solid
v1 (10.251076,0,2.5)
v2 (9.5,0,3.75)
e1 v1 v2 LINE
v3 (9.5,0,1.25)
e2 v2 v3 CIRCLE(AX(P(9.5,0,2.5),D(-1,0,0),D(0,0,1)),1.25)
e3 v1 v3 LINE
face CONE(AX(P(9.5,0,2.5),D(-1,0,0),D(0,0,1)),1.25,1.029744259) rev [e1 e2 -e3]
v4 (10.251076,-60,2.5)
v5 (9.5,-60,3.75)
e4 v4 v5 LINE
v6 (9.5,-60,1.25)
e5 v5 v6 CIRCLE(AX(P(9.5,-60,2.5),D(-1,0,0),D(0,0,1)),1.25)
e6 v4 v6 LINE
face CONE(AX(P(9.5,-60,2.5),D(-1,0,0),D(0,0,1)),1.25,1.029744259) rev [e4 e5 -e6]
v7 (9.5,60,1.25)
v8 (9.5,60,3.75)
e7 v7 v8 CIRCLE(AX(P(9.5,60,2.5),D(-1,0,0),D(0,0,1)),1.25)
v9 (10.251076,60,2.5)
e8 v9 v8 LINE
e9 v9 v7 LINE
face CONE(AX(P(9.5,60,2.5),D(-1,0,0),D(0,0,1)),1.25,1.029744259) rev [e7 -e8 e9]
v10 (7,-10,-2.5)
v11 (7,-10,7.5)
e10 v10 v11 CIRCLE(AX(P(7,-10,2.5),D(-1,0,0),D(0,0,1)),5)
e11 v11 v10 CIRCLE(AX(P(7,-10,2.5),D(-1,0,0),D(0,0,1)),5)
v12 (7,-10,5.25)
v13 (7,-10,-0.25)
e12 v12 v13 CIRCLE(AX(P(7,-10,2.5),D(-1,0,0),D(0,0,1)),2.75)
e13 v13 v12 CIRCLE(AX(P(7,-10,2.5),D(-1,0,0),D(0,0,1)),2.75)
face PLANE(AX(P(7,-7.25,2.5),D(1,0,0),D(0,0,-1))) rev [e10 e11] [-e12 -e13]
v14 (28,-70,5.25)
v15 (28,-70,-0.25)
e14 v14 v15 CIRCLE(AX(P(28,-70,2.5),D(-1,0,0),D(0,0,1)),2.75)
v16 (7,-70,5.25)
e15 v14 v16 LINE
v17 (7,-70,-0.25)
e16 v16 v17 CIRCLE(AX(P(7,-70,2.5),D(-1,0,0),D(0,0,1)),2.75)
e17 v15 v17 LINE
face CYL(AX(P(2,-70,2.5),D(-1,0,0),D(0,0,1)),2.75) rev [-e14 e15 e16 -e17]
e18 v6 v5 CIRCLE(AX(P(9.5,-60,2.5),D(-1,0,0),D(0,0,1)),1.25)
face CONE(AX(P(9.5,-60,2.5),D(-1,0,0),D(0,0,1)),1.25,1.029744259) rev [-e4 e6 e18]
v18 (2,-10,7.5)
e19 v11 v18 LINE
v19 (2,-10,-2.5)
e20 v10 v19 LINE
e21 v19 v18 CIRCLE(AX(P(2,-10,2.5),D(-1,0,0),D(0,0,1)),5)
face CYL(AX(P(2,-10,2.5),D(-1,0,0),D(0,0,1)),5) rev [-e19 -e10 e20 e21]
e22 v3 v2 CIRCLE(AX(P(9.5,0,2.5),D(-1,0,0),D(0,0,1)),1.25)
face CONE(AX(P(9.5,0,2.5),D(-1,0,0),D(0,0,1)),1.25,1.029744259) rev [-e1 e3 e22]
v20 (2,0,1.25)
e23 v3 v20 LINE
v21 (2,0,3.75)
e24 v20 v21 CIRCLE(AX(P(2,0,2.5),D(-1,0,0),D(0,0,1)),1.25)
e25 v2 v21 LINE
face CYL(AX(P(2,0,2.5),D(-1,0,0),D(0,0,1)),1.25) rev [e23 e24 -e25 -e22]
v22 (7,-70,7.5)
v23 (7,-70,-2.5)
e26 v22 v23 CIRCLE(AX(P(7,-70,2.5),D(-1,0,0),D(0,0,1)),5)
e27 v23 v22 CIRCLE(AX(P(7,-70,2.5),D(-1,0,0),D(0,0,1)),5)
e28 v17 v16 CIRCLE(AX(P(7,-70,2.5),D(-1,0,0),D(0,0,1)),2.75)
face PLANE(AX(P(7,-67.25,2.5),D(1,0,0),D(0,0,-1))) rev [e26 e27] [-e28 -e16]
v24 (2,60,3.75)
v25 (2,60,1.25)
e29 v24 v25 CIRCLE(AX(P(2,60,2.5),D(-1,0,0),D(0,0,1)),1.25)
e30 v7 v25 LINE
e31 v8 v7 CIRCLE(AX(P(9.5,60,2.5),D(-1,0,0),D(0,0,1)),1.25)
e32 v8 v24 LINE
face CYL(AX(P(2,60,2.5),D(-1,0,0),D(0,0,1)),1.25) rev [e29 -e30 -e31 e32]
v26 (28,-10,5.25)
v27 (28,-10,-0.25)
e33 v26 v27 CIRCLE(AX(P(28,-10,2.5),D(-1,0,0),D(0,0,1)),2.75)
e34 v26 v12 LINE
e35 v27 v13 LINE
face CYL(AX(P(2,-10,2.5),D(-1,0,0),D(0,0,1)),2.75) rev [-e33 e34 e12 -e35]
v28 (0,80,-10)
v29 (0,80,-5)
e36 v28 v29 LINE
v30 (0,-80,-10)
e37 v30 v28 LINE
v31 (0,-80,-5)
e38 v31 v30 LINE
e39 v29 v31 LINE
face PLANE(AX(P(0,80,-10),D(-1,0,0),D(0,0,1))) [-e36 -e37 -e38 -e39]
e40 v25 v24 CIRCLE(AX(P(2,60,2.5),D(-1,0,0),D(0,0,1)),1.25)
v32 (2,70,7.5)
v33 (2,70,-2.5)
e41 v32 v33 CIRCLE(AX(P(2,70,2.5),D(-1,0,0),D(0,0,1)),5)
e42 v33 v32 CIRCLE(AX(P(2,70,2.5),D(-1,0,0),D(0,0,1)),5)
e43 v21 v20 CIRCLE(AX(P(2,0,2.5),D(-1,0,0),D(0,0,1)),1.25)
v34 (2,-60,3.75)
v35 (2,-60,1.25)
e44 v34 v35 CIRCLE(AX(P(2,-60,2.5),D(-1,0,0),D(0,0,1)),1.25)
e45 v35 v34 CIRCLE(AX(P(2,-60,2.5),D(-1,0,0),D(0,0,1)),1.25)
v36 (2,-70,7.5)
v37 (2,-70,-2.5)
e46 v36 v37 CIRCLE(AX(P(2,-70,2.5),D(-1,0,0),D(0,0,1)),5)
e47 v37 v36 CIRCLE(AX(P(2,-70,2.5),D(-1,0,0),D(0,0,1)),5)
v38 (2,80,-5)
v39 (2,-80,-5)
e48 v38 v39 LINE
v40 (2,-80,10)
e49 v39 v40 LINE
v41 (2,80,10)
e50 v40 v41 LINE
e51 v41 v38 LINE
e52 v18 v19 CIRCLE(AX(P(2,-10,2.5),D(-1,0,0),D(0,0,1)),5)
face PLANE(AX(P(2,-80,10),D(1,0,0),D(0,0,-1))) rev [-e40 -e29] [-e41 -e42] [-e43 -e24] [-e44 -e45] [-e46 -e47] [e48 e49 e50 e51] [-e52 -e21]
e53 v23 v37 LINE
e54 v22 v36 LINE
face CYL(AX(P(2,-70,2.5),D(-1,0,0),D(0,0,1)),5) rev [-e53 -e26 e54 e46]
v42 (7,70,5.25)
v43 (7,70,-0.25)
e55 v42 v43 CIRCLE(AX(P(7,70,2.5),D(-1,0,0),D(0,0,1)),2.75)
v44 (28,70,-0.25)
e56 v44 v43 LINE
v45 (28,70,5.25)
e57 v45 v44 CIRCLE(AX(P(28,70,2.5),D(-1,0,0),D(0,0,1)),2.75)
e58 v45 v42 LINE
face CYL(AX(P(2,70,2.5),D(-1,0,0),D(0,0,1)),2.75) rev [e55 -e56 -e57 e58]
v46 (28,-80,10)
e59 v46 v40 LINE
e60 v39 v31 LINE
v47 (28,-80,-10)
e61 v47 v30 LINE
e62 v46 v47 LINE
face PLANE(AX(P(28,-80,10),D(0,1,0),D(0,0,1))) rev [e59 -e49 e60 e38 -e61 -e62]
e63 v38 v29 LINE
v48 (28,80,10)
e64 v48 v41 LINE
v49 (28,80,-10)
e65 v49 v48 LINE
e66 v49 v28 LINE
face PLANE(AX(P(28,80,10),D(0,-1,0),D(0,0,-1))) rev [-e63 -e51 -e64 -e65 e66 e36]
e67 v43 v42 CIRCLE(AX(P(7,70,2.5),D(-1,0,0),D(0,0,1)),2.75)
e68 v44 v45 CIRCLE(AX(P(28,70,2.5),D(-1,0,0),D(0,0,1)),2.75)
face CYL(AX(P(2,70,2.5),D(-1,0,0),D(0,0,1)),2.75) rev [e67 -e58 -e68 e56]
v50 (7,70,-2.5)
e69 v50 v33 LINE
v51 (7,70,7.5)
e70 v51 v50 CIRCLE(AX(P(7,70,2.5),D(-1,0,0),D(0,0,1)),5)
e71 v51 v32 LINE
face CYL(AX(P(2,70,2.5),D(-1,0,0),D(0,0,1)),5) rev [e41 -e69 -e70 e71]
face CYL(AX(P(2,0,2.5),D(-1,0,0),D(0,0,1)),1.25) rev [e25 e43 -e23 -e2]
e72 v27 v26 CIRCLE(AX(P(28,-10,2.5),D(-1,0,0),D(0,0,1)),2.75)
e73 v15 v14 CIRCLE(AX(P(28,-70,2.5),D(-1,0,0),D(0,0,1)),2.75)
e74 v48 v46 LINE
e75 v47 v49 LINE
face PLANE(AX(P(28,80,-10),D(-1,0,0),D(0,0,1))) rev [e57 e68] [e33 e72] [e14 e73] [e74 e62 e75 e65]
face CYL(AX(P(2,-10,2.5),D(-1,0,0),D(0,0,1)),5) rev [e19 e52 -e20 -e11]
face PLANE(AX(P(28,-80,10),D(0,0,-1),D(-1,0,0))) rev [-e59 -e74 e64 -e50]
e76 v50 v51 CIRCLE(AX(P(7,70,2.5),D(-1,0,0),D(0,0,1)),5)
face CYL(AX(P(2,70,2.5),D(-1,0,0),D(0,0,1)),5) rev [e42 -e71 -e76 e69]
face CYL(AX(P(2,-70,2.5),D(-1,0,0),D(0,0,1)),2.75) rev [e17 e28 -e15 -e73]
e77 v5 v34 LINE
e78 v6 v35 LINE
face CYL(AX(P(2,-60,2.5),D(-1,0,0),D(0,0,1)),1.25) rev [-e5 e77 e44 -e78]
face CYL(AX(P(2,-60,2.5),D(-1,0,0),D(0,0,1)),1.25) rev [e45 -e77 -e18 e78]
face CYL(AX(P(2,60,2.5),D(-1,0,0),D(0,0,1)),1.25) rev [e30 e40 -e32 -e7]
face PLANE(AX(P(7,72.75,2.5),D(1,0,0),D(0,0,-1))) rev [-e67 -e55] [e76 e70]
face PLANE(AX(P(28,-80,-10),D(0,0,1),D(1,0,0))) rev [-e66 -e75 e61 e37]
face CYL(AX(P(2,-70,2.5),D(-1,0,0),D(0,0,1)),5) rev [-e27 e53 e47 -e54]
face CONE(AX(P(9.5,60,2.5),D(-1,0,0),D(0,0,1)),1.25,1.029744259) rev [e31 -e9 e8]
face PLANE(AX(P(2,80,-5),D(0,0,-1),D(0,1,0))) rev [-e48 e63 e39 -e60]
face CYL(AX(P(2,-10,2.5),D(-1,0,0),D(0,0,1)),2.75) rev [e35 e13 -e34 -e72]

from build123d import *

# Parameters (mm, degrees)
SKETCH_1_W                                         = 20
SKETCH_1_H                                         = 160
BOSS_EXTRUDE_1_DEPTH                               = 28
SKETCH_2_W                                         = 15
SKETCH_2_H                                         = 160
CUT_EXTRUDE_1_DEPTH                                = 2
LINEAR_PATTERN_1_COUNT                             = 3
LINEAR_PATTERN_1_PITCH                             = 60
M5_SOCKET_HEAD_CAP_SCREW_COUNTERBORE_1_D           = 5.5
M5_SOCKET_HEAD_CAP_SCREW_COUNTERBORE_1_CBORE_D     = 10
M5_SOCKET_HEAD_CAP_SCREW_COUNTERBORE_1_CBORE_DEPTH = 5
LINEAR_PATTERN_2_COUNT                             = 2
LINEAR_PATTERN_2_PITCH                             = 140
LINEAR_PATTERN_3_COUNT                             = 2
LINEAR_PATTERN_3_PITCH                             = 60


with BuildPart() as part:
    # Sketch 1 → Boss-Extrude 1 (new body)
    with BuildSketch(Plane(origin=(0, 0, 0), x_dir=(0, 0, -1), z_dir=(1, 0, 0))):
        Rectangle(SKETCH_1_W, SKETCH_1_H)
    extrude(amount=BOSS_EXTRUDE_1_DEPTH)

    # Sketch 2 → Cut-Extrude 1 (cut)
    with BuildSketch(Plane.ZY):
        with Locations((2.5, 0)):
            Rectangle(SKETCH_2_W, SKETCH_2_H)
    extrude(amount=-CUT_EXTRUDE_1_DEPTH, mode=Mode.SUBTRACT)

    # Sketch 3 → M3 Tapped Hole 1 (revolve, cut)
    with BuildSketch(Plane(origin=(2, -60, 2.5), x_dir=(0, 0, 1), z_dir=(0, 1, 0))):
        Polygon((0, 0), (0, 8.251075774), (1.25, 7.5), (1.25, 0), align=None)
    m3_tapped_hole_1 = revolve(axis=Axis((-4.35, -60, 2.5), (1, 0, 0)), mode=Mode.SUBTRACT)

    # Linear Pattern 1: M3 Tapped Hole 1 ×3
    with Locations(*[(0, i * LINEAR_PATTERN_1_PITCH, 0) for i in range(1, LINEAR_PATTERN_1_COUNT)]):
        add(m3_tapped_hole_1, mode=Mode.SUBTRACT)

    # M5 Socket Head Cap Screw Counterbore 1 (through all)
    with Locations(Plane.ZY.offset(-2)):
        with Locations((2.5, -70)):
            m5_socket_head_cap_screw_counterbore_1 = CounterBoreHole(M5_SOCKET_HEAD_CAP_SCREW_COUNTERBORE_1_D / 2, M5_SOCKET_HEAD_CAP_SCREW_COUNTERBORE_1_CBORE_D / 2, M5_SOCKET_HEAD_CAP_SCREW_COUNTERBORE_1_CBORE_DEPTH)

    # Linear Pattern 2: M5 Socket Head Cap Screw Counterbore 1 ×2
    with Locations(*[(0, i * LINEAR_PATTERN_2_PITCH, 0) for i in range(1, LINEAR_PATTERN_2_COUNT)]):
        add(m5_socket_head_cap_screw_counterbore_1, mode=Mode.SUBTRACT)

    # Linear Pattern 3: M5 Socket Head Cap Screw Counterbore 1 ×2
    with Locations(*[(0, i * LINEAR_PATTERN_3_PITCH, 0) for i in range(1, LINEAR_PATTERN_3_COUNT)]):
        add(m5_socket_head_cap_screw_counterbore_1, mode=Mode.SUBTRACT)


solid = part.part
